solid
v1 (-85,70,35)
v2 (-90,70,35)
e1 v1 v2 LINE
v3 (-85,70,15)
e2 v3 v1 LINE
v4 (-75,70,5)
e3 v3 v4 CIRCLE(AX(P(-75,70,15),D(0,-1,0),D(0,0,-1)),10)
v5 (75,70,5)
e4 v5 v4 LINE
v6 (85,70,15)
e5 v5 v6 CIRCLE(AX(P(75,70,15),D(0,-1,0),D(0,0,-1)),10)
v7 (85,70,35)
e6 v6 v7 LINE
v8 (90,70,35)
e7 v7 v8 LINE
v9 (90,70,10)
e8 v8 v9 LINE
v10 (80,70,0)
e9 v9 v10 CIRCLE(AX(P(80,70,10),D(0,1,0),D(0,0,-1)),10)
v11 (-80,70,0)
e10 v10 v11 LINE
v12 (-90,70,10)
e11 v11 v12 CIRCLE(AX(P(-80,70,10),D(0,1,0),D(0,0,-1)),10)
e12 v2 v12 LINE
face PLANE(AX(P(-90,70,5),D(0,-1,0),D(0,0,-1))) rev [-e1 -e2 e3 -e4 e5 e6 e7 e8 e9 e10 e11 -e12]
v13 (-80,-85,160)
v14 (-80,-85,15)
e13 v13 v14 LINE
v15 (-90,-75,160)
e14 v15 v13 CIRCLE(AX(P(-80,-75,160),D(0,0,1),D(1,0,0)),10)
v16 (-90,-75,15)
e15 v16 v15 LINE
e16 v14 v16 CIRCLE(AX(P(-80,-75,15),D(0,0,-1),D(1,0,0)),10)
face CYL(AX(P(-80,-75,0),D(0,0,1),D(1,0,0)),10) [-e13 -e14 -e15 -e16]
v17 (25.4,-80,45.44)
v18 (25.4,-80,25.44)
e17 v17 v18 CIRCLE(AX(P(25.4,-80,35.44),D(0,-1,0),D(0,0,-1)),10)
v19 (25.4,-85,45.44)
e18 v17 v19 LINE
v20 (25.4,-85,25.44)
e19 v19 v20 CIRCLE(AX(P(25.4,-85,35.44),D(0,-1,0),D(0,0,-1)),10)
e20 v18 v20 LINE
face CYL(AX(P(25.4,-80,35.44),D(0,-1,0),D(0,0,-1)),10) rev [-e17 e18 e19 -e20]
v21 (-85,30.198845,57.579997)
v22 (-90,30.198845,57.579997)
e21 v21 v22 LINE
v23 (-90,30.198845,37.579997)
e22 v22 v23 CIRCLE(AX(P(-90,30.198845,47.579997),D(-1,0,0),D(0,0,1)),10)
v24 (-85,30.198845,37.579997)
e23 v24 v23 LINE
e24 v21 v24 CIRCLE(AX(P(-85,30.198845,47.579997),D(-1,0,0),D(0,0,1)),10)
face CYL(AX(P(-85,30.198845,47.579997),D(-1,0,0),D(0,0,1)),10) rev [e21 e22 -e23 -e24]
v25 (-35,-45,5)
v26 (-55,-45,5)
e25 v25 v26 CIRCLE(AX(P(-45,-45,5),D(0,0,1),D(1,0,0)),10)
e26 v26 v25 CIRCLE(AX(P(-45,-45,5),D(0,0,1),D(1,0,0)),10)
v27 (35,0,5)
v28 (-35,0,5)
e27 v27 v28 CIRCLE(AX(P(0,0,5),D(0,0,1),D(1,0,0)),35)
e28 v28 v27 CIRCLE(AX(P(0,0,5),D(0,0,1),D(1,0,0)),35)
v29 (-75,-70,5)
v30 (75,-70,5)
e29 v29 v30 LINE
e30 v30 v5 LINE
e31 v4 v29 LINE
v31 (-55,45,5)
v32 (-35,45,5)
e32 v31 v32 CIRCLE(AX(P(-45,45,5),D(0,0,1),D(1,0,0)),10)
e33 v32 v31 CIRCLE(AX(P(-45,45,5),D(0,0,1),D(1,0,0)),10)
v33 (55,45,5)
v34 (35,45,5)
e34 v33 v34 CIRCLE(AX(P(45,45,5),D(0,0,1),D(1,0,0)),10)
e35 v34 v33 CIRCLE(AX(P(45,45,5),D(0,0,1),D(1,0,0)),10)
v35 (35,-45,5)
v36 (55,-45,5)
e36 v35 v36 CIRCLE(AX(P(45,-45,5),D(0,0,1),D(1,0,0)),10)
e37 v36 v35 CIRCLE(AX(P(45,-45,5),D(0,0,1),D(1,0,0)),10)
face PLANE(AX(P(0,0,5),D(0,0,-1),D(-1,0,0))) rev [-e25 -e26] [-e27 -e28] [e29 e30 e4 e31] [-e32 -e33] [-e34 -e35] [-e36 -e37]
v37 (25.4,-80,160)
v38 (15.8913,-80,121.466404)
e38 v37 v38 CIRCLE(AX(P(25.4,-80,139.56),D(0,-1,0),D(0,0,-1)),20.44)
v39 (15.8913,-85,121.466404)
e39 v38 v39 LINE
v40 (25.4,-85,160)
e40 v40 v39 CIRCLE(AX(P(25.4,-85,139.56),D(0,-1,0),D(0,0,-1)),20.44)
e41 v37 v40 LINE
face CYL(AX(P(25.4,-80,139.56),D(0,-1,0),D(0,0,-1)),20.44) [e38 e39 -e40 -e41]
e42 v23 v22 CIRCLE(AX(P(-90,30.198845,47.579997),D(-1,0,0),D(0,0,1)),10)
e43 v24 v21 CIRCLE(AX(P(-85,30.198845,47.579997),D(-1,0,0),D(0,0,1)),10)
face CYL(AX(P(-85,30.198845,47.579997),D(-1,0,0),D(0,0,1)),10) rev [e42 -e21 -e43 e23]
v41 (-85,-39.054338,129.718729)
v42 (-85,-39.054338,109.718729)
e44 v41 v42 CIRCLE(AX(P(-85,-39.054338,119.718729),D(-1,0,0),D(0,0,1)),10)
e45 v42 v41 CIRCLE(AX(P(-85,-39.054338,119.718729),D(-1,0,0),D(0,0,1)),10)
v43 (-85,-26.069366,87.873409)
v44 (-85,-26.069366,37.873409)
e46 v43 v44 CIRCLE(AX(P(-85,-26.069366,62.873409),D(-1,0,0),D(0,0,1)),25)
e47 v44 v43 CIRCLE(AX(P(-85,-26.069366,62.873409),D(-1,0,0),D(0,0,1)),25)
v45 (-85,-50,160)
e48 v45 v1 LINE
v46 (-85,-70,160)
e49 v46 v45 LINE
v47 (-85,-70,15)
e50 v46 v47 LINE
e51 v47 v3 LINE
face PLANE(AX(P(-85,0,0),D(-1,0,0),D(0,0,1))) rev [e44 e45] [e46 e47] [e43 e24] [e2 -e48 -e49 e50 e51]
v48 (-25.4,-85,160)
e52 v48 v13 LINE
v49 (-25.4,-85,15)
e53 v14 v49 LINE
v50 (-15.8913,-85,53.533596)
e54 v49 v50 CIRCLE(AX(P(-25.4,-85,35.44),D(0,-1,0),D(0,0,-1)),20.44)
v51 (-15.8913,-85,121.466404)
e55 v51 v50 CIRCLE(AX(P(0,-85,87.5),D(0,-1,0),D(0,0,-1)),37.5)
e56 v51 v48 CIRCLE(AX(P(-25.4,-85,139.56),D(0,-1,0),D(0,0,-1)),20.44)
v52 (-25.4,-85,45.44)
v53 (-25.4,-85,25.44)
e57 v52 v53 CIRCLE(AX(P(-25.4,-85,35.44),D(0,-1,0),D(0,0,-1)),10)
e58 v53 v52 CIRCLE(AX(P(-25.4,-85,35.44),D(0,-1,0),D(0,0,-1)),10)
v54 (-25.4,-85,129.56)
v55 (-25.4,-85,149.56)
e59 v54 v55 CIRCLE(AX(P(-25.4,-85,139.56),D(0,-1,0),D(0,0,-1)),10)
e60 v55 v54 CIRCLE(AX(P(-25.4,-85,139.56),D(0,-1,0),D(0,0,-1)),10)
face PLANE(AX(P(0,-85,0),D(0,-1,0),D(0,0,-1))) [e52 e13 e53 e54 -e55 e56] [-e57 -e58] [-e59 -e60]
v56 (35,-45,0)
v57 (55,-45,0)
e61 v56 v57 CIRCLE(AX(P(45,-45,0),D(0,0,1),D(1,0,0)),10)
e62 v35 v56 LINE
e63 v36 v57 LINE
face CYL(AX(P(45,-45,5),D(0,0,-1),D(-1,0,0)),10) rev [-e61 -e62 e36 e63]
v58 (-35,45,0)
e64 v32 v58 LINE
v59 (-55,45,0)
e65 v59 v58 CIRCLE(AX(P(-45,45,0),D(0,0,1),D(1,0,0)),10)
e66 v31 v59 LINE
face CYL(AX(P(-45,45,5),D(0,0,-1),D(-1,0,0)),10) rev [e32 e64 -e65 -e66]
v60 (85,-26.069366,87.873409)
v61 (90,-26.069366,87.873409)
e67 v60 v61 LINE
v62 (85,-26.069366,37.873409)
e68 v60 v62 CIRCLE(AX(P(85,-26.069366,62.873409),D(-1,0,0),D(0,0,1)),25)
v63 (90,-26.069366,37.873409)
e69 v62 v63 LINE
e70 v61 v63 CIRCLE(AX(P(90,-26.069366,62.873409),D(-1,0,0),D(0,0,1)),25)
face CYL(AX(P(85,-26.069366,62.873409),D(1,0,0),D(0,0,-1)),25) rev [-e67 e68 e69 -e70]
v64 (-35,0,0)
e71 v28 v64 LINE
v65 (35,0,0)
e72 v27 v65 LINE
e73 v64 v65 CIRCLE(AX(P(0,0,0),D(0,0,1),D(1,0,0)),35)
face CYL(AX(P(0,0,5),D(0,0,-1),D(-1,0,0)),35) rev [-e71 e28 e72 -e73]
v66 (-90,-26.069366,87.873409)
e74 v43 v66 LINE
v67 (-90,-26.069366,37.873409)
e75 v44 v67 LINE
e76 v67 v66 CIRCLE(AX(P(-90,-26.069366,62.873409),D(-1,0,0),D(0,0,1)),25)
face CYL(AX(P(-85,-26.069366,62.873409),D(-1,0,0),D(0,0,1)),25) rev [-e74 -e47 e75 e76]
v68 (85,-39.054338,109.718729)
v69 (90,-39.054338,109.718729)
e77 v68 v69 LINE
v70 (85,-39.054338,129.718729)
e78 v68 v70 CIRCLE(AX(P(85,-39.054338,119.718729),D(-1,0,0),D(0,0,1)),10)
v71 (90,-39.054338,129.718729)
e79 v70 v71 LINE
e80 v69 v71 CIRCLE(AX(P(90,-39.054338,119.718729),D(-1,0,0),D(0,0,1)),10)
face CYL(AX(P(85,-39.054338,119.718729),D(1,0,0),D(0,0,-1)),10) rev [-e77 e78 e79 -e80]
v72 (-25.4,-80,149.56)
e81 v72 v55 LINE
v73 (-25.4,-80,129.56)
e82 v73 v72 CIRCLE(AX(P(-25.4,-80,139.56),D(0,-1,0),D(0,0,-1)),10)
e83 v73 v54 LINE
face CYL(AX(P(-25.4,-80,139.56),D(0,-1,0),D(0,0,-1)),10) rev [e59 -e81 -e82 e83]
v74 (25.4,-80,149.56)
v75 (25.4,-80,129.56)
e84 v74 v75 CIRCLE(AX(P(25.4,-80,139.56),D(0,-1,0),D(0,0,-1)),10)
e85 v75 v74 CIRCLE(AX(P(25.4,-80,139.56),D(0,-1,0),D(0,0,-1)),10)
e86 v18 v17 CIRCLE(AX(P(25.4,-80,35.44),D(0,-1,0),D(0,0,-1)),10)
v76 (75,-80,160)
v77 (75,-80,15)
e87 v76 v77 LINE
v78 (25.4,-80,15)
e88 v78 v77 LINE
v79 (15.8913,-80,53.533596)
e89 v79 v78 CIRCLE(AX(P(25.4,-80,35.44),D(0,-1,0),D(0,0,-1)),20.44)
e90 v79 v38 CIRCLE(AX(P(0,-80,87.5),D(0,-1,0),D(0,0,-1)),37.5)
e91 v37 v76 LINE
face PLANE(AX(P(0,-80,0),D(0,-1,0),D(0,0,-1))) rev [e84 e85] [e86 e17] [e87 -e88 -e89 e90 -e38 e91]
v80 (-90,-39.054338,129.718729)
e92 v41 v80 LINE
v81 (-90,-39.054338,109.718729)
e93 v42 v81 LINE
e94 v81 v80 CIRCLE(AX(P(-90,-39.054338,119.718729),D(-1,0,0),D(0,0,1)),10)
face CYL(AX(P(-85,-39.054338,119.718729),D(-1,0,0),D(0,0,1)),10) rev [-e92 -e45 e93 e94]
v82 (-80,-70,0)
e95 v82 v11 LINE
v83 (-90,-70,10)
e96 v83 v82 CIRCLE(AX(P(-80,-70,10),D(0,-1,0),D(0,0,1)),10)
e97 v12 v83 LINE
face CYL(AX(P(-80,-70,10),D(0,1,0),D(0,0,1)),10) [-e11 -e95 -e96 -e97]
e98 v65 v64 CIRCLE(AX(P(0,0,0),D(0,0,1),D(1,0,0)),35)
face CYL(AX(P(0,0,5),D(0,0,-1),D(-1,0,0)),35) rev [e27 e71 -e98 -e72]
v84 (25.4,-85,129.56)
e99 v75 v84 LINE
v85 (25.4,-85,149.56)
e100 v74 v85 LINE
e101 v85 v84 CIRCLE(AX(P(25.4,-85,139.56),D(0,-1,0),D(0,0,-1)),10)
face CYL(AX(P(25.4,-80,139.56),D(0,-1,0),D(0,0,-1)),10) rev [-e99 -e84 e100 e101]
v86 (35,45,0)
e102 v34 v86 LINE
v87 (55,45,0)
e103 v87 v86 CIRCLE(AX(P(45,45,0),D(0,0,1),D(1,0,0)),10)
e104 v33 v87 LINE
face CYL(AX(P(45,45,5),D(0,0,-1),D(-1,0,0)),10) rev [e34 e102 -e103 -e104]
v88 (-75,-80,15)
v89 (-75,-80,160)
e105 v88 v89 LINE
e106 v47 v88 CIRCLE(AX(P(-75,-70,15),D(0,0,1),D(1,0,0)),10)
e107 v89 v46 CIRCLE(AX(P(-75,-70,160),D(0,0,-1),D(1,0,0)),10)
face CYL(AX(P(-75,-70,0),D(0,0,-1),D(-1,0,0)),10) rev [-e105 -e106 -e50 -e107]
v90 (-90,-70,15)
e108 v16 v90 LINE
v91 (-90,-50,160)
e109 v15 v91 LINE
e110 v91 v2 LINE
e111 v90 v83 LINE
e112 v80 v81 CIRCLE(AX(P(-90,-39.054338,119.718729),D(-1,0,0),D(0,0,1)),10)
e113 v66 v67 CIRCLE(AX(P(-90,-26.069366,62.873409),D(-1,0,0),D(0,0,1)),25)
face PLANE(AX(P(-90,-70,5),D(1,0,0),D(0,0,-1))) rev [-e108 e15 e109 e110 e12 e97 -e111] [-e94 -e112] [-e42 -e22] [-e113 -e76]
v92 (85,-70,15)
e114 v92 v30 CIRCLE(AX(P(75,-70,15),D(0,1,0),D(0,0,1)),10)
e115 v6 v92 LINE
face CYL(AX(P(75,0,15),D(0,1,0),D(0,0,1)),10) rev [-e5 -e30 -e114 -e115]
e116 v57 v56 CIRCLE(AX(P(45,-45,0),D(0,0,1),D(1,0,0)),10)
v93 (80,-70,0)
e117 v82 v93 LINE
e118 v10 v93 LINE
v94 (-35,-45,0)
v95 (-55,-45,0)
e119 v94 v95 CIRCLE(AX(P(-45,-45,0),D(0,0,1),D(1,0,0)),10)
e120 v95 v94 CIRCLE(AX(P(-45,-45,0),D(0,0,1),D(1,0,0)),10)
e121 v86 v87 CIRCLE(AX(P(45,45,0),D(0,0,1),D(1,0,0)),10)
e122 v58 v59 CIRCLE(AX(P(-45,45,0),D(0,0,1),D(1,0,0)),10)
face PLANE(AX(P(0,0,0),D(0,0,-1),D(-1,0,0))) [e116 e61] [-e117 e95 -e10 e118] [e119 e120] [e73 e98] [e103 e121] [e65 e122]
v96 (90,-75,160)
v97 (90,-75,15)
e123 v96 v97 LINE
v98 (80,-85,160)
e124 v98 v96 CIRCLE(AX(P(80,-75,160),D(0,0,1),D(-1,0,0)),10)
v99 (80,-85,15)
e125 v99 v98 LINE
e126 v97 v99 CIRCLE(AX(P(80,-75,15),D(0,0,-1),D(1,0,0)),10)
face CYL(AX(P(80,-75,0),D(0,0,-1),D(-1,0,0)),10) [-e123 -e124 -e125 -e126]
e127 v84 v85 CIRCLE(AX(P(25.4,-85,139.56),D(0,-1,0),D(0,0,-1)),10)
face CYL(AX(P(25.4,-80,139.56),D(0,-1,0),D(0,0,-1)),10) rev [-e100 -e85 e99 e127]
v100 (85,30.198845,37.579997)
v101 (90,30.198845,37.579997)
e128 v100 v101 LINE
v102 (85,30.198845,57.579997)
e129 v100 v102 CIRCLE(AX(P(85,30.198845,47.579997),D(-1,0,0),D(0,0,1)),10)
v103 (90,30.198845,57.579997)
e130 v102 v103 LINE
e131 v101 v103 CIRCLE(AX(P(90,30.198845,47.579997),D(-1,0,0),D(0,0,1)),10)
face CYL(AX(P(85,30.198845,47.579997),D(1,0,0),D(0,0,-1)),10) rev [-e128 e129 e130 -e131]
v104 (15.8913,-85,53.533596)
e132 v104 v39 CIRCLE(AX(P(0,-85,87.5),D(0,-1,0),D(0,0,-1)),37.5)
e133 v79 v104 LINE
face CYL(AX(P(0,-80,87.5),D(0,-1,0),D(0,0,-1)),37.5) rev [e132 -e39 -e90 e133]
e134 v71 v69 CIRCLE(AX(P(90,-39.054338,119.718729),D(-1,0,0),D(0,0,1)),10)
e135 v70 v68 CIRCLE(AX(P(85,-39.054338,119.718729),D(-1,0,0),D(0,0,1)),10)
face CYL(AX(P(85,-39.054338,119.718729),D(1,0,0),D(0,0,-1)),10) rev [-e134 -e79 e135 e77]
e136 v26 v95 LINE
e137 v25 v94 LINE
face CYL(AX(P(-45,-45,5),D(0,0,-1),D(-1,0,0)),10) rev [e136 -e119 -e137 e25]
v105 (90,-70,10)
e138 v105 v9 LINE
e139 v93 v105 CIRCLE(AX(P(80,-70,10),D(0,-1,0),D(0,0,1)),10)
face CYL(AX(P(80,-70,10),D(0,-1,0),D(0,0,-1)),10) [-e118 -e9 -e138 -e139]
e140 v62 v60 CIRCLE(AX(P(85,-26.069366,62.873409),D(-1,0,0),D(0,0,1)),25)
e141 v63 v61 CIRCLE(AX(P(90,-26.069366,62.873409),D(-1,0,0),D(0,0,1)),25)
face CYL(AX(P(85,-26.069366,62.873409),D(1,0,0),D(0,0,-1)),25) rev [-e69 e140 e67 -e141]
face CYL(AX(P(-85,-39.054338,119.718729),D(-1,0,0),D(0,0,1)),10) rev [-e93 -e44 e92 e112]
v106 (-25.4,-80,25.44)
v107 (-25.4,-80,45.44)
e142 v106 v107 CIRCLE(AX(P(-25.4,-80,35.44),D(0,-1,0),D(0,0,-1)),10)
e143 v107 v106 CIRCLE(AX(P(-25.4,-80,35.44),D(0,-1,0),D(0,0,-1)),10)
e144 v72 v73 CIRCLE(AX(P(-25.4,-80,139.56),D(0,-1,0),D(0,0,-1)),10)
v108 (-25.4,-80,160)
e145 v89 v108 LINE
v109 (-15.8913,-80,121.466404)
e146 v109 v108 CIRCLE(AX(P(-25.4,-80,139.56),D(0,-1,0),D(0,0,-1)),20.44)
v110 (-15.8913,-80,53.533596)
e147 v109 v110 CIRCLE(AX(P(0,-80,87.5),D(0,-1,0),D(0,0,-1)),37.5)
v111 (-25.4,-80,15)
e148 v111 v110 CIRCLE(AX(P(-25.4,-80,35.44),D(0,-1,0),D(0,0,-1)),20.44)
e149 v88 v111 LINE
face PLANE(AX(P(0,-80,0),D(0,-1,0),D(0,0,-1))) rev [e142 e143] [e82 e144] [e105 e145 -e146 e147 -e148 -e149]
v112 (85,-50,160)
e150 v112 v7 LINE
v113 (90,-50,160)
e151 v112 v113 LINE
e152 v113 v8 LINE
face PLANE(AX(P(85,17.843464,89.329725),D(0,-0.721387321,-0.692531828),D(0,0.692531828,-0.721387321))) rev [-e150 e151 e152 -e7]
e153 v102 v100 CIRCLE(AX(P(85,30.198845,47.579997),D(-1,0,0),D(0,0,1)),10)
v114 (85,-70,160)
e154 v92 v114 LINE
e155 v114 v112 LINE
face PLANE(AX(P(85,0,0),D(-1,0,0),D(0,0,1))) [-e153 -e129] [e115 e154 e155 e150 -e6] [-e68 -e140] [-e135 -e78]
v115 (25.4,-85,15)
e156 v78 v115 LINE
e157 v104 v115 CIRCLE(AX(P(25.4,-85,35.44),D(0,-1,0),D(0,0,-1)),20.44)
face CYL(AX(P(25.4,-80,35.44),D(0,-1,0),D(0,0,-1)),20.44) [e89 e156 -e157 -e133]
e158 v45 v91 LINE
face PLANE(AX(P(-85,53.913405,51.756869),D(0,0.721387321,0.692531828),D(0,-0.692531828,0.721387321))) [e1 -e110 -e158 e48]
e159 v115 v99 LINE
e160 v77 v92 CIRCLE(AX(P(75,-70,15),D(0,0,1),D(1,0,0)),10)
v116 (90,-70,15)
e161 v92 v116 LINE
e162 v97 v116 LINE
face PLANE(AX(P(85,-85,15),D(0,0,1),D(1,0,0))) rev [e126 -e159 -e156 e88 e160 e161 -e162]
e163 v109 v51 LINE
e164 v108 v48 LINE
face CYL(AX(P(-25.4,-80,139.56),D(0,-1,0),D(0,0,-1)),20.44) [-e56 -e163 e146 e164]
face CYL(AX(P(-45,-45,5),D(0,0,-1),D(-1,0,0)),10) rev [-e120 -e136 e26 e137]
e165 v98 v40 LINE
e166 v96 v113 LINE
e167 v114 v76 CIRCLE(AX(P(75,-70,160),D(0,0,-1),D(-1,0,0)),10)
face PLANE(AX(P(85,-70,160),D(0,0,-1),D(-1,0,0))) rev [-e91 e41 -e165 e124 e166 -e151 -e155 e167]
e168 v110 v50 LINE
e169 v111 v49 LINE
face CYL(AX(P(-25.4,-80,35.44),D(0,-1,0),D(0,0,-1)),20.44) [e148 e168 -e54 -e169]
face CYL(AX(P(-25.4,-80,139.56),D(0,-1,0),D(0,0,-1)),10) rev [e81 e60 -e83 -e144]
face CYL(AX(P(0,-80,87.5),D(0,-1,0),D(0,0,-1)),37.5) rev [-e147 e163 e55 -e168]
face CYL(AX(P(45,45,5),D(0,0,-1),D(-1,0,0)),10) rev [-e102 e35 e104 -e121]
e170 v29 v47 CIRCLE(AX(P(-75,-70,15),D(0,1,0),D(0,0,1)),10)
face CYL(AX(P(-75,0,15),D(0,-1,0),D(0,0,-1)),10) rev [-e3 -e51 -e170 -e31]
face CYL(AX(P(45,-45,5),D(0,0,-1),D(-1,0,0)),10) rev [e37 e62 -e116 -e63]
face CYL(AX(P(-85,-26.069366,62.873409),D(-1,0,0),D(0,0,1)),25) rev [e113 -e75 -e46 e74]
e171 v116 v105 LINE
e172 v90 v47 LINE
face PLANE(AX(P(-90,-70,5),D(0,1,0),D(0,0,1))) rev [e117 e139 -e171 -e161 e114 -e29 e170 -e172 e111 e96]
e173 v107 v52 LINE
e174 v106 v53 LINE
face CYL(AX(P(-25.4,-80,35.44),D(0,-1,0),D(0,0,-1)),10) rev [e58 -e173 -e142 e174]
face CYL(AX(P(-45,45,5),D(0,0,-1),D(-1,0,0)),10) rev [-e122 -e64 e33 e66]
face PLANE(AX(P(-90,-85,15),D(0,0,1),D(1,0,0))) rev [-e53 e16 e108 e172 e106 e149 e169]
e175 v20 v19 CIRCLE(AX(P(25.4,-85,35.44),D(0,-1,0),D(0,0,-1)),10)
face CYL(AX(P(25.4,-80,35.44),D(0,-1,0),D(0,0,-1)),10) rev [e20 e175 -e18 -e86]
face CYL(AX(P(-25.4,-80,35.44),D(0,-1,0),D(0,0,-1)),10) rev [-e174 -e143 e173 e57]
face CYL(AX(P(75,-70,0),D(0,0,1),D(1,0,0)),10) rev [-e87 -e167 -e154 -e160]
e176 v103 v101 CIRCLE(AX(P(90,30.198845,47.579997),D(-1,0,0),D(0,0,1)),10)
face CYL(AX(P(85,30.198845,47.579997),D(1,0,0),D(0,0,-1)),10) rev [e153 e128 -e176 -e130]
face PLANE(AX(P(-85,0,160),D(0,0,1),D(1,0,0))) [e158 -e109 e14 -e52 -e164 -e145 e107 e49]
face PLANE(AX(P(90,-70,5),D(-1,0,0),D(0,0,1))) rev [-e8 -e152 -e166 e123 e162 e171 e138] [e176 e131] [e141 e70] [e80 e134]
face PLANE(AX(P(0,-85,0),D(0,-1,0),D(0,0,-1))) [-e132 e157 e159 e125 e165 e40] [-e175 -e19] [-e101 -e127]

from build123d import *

# Parameters (mm, degrees)
BASE_FLANGE_SKETCH_W     = 180
BASE_FLANGE_SKETCH_H     = 140
BASE_FLANGE_SKETCH_R     = 35
BASE_FLANGE_SKETCH_R_2   = 10
BASE_FLANGE_5MM_DEPTH    = 5
SIDE_GUSSET_SKETCH_R     = 25
SIDE_GUSSET_SKETCH_R_2   = 10
SIDE_GUSSET_SKETCH_W     = 5
SIDE_GUSSET_SKETCH_H     = 140
SIDE_GUSSET_A_DEPTH      = 5
SIDE_START               = -175
SKETCH2_5_R              = 25
SKETCH2_5_R_2            = 10
SKETCH2_5_W              = 5
SKETCH2_5_H              = 140
SIDE_GUSSET_B_DEPTH      = 5
BASE_FLANGE_FILLET_R10_R = 10
GUSSET_EDGE_FILLET_R10_R = 10
BACK_PLATE_SKETCH_W      = 5
BACK_PLATE_SKETCH_H      = 145
BACK_PLATE_DEPTH         = 15
MOTOR_MOUNT_PAD_SKETCH_R = 10
MOTOR_MOUNT_PAD_SKETCH_W = 5
MOTOR_MOUNT_PAD_SKETCH_H = 145
MOTOR_MOUNT_PAD_DEPTH    = 5
MOUNT_EDGE_FILLET_R10_R  = 10


with BuildPart() as part:
    # Base Flange Sketch → Base Flange 5mm (new body)
    with BuildSketch(Plane.XY):
        Rectangle(BASE_FLANGE_SKETCH_W, BASE_FLANGE_SKETCH_H)
        Circle(BASE_FLANGE_SKETCH_R, mode=Mode.SUBTRACT)
        with Locations((-45, 45)):
            Circle(BASE_FLANGE_SKETCH_R_2, mode=Mode.SUBTRACT)
        with Locations((45, 45)):
            Circle(BASE_FLANGE_SKETCH_R_2, mode=Mode.SUBTRACT)
        with Locations((-45, -45)):
            Circle(BASE_FLANGE_SKETCH_R_2, mode=Mode.SUBTRACT)
        with Locations((45, -45)):
            Circle(BASE_FLANGE_SKETCH_R_2, mode=Mode.SUBTRACT)
    extrude(amount=BASE_FLANGE_5MM_DEPTH)

    # Side Gusset Sketch → Side Gusset A (add)
    # profile 1 of 2: a face of its own
    with BuildSketch(Plane.ZY.offset(90)):
        Polygon((35, 70), (5, 70), (5, -70), (160, -70), (160, -50), (133.569366052, -24.626591409), (97.5, 10), (61.430633948, 44.626591409), align=None)
        with Locations((62.873408591, -26.069366052)):
            Circle(SIDE_GUSSET_SKETCH_R, mode=Mode.SUBTRACT)
        with Locations((119.718729488, -39.05433783)):
            Circle(SIDE_GUSSET_SKETCH_R_2, mode=Mode.SUBTRACT)
        with Locations((47.579997385, 30.198844989)):
            Circle(SIDE_GUSSET_SKETCH_R_2, mode=Mode.SUBTRACT)
    # profile 2 of 2: a face of its own
    with BuildSketch(Plane.ZY.offset(90)):
        with Locations((2.5, 0)):
            Rectangle(SIDE_GUSSET_SKETCH_W, SIDE_GUSSET_SKETCH_H)
    extrude(amount=-SIDE_GUSSET_A_DEPTH)

    # Sketch2_5 → Side Gusset B (add)
    # profile 1 of 2: a face of its own
    with BuildSketch(Plane.ZY.offset(90).offset(SIDE_START)):
        Polygon((35, 70), (5, 70), (5, -70), (160, -70), (160, -50), (133.569366052, -24.626591409), (97.5, 10), (61.430633948, 44.626591409), align=None)
        with Locations((62.873408591, -26.069366052)):
            Circle(SKETCH2_5_R, mode=Mode.SUBTRACT)
        with Locations((119.718729488, -39.05433783)):
            Circle(SKETCH2_5_R_2, mode=Mode.SUBTRACT)
        with Locations((47.579997385, 30.198844989)):
            Circle(SKETCH2_5_R_2, mode=Mode.SUBTRACT)
    # profile 2 of 2: a face of its own
    with BuildSketch(Plane.ZY.offset(90).offset(SIDE_START)):
        with Locations((2.5, 0)):
            Rectangle(SKETCH2_5_W, SKETCH2_5_H)
    extrude(amount=-SIDE_GUSSET_B_DEPTH)

    # Base Flange Fillet R10
    base_flange_fillet_r10_edges = [part.edges().sort_by_distance(p)[0] for p in [
        (-90, 0, 0),
        (90, 0, 0),
    ]]
    fillet(base_flange_fillet_r10_edges, radius=BASE_FLANGE_FILLET_R10_R)

    # Gusset Edge Fillet R10
    gusset_edge_fillet_r10_edges = [part.edges().sort_by_distance(p)[0] for p in [
        (-85, 0, 5),
        (85, 0, 5),
    ]]
    fillet(gusset_edge_fillet_r10_edges, radius=GUSSET_EDGE_FILLET_R10_R)

    # Back Plate Sketch → Back Plate (add)
    with BuildSketch(Plane.XZ.offset(70)):
        with Locations((-87.5, 87.5)):
            Rectangle(BACK_PLATE_SKETCH_W, BACK_PLATE_SKETCH_H)
        with Locations((87.5, 87.5)):
            Rectangle(BACK_PLATE_SKETCH_W, BACK_PLATE_SKETCH_H)
    extrude(amount=BACK_PLATE_DEPTH)

    # Motor Mount Pad Sketch → Motor Mount Pad (add)
    # profile 1 of 3: a face of its own
    with BuildSketch(Plane.XZ.offset(85)):
        with BuildLine():
            Line((-25.4, 160), (-85, 160))
            Line((-85, 160), (-85, 15))
            Line((-85, 15), (-25.4, 15))
            ThreePointArc((-25.4, 15), (-5.555268835, 30.543037168), (-15.891300301, 53.533596382))
            ThreePointArc((-15.891300301, 53.533596382), (-16.443437096, 53.797427747), (-16.991195266, 54.070233572))
            ThreePointArc((-16.991195266, 54.070233572), (-37.5, 87.5), (-16.991195266, 120.929766428))
            ThreePointArc((-16.991195266, 120.929766428), (-16.443437096, 121.202572253), (-15.891300301, 121.466403618))
            ThreePointArc((-15.891300301, 121.466403618), (-5.555268835, 144.456962832), (-25.4, 160))
        make_face()
        with Locations(Location((-25.4, 35.44, 0), (0, 0, 270))):
            Circle(MOTOR_MOUNT_PAD_SKETCH_R, mode=Mode.SUBTRACT)
        with Locations(Location((-25.4, 139.56, 0), (0, 0, 270))):
            Circle(MOTOR_MOUNT_PAD_SKETCH_R, mode=Mode.SUBTRACT)
    # profile 2 of 3: a face of its own
    with BuildSketch(Plane.XZ.offset(85)):
        with BuildLine():
            Line((90, 160), (25.4, 160))
            ThreePointArc((25.4, 160), (5.555268835, 144.456962832), (15.891300301, 121.466403618))
            ThreePointArc((15.891300301, 121.466403618), (16.443437096, 121.202572253), (16.991195266, 120.929766428))
            ThreePointArc((16.991195266, 120.929766428), (37.5, 87.5), (16.991195266, 54.070233572))
            ThreePointArc((16.991195266, 54.070233572), (16.443437096, 53.797427747), (15.891300301, 53.533596382))
            ThreePointArc((15.891300301, 53.533596382), (5.555268835, 30.543037168), (25.4, 15))
            Line((25.4, 15), (90, 15))
            Line((90, 15), (90, 160))
        make_face()
        with Locations(Location((25.4, 35.44, 0), (0, 0, 270))):
            Circle(MOTOR_MOUNT_PAD_SKETCH_R, mode=Mode.SUBTRACT)
        with Locations(Location((25.4, 139.56, 0), (0, 0, 270))):
            Circle(MOTOR_MOUNT_PAD_SKETCH_R, mode=Mode.SUBTRACT)
    # profile 3 of 3: a face of its own
    with BuildSketch(Plane.XZ.offset(85)):
        with Locations((-87.5, 87.5)):
            Rectangle(MOTOR_MOUNT_PAD_SKETCH_W, MOTOR_MOUNT_PAD_SKETCH_H)
    extrude(amount=-MOTOR_MOUNT_PAD_DEPTH)

    # Mount Edge Fillet R10
    mount_edge_fillet_r10_edges = [part.edges().sort_by_distance(p)[0] for p in [
        (85, -80, 87.5),
        (90, -85, 87.5),
        (-90, -85, 87.5),
        (-85, -80, 87.5),
    ]]
    fillet(mount_edge_fillet_r10_edges, radius=MOUNT_EDGE_FILLET_R10_R)


solid = part.part
